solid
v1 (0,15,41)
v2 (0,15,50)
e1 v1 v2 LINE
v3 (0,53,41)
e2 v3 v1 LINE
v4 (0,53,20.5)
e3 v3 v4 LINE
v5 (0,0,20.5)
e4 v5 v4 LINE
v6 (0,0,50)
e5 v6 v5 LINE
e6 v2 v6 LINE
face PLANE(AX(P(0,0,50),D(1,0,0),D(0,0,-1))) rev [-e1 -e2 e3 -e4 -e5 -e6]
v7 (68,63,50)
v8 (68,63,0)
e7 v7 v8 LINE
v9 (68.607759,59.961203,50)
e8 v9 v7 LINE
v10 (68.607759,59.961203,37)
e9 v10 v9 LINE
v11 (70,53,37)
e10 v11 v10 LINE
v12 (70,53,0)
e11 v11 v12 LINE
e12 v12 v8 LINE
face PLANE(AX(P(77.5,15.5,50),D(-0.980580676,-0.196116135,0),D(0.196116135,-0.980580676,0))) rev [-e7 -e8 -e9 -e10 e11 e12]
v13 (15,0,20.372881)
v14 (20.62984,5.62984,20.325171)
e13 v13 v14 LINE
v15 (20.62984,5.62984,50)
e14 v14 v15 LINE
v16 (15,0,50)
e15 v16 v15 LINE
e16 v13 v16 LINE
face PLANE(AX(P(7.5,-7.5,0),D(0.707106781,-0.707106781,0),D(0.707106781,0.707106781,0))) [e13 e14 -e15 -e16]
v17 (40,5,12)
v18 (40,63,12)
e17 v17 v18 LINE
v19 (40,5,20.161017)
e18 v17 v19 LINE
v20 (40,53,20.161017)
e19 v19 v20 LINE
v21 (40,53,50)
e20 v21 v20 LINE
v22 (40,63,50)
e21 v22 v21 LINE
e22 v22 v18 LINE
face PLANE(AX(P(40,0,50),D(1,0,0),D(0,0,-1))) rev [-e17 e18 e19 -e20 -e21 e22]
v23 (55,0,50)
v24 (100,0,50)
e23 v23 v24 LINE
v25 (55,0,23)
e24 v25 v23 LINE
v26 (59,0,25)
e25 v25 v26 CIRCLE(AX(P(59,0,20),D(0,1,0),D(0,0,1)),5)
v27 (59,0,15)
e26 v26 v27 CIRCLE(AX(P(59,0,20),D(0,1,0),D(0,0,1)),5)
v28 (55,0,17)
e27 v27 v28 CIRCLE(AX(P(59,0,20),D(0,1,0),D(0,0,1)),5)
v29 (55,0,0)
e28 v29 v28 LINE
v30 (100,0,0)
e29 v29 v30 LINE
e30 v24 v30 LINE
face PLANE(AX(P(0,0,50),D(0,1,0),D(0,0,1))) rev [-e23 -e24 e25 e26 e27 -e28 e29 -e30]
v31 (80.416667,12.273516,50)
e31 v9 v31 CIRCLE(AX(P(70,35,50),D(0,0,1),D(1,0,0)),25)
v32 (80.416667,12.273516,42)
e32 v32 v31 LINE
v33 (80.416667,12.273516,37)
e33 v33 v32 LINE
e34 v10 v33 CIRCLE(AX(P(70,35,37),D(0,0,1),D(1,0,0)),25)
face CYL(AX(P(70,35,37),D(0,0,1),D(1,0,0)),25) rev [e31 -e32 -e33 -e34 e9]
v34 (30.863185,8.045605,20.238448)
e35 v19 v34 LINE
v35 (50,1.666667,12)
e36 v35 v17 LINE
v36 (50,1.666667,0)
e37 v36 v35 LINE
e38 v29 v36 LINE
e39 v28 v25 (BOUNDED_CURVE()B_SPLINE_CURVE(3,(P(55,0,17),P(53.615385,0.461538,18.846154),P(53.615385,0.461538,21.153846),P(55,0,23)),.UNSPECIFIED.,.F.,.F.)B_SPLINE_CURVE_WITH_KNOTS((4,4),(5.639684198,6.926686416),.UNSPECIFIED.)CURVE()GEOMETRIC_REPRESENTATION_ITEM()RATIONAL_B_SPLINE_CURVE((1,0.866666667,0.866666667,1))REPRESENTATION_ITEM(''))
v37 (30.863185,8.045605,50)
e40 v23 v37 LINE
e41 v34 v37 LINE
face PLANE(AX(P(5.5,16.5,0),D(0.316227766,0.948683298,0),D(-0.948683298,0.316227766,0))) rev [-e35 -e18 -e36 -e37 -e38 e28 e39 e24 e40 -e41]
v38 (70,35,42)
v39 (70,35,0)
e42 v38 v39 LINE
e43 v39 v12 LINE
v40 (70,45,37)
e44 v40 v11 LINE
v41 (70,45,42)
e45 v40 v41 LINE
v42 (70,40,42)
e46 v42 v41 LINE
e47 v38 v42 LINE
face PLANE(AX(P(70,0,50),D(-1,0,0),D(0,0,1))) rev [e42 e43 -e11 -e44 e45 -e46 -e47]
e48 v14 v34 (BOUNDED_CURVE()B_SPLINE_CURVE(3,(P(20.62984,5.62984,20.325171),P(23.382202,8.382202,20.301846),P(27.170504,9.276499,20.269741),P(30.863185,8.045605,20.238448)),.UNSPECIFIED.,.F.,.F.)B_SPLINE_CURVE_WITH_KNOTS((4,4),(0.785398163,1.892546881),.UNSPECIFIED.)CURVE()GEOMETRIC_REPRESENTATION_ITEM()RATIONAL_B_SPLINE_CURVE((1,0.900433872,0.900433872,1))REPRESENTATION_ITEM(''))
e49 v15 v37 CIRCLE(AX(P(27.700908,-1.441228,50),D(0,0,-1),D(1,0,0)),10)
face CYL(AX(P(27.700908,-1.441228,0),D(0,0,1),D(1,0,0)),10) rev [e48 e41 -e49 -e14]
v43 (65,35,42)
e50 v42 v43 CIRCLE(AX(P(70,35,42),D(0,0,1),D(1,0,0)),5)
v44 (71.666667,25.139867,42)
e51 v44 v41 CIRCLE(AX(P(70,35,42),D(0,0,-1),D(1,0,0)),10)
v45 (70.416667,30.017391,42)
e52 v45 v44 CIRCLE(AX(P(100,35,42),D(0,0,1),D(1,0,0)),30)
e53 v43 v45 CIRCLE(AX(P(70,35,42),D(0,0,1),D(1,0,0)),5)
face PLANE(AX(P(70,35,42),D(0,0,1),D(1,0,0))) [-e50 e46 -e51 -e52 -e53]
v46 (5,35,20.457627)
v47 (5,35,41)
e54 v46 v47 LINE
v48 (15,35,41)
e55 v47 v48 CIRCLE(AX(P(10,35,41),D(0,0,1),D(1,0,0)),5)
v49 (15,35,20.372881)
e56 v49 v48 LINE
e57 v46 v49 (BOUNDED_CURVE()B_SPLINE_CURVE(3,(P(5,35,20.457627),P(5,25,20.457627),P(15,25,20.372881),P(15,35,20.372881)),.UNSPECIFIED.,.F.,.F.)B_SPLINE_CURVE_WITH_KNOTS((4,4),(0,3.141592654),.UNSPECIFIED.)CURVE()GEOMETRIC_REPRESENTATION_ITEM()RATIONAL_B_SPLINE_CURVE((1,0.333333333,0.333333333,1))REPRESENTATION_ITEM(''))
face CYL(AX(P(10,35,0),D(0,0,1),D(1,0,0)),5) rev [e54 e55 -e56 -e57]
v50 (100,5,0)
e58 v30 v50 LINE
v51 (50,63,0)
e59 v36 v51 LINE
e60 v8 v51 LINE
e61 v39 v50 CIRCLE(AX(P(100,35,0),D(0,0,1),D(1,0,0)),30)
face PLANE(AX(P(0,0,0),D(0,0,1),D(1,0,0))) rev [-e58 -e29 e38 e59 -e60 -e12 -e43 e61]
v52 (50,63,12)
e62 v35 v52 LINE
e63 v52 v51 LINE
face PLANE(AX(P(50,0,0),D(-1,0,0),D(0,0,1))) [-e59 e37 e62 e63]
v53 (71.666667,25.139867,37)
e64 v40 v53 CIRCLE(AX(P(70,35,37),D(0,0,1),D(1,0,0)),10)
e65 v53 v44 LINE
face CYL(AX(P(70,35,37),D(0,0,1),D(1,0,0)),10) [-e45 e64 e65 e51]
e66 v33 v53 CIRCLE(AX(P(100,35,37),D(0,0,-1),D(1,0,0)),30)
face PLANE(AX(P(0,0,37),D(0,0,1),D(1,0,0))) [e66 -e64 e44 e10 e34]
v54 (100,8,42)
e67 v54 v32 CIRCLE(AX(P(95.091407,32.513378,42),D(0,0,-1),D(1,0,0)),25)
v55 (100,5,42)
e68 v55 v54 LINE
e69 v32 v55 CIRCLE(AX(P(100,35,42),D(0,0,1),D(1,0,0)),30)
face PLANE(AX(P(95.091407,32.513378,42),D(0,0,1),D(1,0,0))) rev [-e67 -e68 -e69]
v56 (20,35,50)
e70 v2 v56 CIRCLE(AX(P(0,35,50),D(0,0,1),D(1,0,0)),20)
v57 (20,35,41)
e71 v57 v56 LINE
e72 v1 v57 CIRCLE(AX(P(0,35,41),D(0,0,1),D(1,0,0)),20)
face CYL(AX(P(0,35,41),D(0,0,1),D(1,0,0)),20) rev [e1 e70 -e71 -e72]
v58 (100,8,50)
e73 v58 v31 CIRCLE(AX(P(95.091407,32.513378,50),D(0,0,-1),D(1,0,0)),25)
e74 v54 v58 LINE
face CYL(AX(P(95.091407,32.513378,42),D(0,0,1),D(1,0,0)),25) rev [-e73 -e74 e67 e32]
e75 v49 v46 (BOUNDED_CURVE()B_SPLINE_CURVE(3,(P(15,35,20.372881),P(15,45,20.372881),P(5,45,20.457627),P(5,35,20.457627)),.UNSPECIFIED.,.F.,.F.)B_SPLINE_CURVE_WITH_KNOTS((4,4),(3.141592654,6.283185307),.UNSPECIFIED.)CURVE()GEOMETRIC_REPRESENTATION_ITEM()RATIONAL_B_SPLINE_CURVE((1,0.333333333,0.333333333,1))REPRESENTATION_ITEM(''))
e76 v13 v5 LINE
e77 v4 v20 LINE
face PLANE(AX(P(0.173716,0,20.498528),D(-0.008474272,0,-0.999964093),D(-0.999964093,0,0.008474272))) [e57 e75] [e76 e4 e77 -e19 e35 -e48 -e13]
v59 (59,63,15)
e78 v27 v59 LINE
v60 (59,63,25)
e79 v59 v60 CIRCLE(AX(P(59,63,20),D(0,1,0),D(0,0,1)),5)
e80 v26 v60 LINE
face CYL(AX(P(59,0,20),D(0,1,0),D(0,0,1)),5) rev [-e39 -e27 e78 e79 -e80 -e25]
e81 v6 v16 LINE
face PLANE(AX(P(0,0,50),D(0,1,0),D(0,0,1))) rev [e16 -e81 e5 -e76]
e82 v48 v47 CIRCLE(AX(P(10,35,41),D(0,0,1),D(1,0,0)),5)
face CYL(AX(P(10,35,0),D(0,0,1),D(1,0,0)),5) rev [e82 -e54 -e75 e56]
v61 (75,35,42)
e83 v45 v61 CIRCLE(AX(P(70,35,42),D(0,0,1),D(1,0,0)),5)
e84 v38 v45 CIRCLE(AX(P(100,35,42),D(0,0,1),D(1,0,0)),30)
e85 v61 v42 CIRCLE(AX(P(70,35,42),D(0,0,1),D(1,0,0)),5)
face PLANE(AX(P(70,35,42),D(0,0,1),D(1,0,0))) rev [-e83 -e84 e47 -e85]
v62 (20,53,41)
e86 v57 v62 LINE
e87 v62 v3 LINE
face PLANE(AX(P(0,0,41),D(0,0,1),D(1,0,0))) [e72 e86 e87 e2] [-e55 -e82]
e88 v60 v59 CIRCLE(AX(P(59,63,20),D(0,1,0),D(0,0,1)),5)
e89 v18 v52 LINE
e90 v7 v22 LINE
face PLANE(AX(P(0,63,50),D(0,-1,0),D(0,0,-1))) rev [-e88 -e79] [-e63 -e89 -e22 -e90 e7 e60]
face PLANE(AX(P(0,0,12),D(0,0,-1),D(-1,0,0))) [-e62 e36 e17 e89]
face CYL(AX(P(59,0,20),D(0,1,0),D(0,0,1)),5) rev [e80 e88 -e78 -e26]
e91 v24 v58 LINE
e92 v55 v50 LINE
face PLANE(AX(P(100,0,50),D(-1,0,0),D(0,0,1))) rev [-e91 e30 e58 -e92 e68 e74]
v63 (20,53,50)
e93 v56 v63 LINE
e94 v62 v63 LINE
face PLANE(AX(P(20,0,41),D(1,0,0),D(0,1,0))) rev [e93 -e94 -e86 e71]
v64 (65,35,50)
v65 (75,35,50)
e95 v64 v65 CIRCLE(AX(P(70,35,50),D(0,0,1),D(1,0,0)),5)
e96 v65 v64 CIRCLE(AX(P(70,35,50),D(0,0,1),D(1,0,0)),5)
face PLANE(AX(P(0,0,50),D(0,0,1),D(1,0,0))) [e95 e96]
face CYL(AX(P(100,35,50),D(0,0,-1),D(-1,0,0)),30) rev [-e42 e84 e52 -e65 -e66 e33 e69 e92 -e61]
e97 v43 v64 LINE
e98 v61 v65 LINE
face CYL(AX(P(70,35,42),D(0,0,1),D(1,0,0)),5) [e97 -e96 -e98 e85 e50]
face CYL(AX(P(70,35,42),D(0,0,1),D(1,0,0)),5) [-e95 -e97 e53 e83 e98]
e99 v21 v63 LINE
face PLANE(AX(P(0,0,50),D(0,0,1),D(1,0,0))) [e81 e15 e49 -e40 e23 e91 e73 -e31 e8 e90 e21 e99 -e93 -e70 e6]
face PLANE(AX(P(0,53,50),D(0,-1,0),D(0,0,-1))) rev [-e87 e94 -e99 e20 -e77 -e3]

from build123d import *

# Parameters (mm, degrees)
BLOCK_BODY_DEPTH          = 50
BEARING_START             = -13
BEARING_ARC_RECESS_DEPTH  = 13
ARC_POCKET_SKETCH_R       = 10.03476875
ARC_POCKET_SKETCH_R_2     = 5
ARC_POCKET_DEPTH          = 8
PIN_10_SKETCH_R           = 5
PIN_10_DEPTH              = 8
SIDE_BOSS_DEPTH           = 8
PROFILE_RELIEF_CUT_DEPTH  = 129.33160172
STEP_CUT_DEPTH            = 9
STEP_NOTCH_DEPTH          = 126.099960032
SLOT_CUT_SKETCH_R         = 5
SLOT_CUT_DEPTH            = 129.33160172
TOP_RELIEF_CUT_DEPTH      = 129.33160172
TOP_RELIEF_CUT_DEPTH_BACK = 129.33160172
TOP_RELIEF_SKETCH_W       = 10
TOP_RELIEF_SKETCH_H       = 12


with BuildPart() as part:
    # Block Profile Sketch → Block Body (new body)
    with BuildSketch(Plane.XY):
        with BuildLine():
            ThreePointArc((70, 35), (78.786796564, 13.786796564), (100, 5))
            Line((100, 5), (100, 0))
            Line((100, 0), (0, 0))
            Line((0, 0), (0, 53))
            Line((0, 53), (40, 53))
            Line((40, 53), (40, 63))
            Line((40, 63), (50, 63))
            Line((50, 63), (68, 63))
            Line((68, 63), (70, 53))
            Line((70, 53), (70, 35))
        make_face()
    extrude(amount=BLOCK_BODY_DEPTH)

    # Bearing Arc Recess Sketch → Bearing Arc Recess (cut)
    with BuildSketch(Plane.XY.offset(50).offset(BEARING_START)):
        with BuildLine():
            ThreePointArc((80.416666667, 12.273516428), (91.040635288, 21.498456878), (95, 35))
            ThreePointArc((95, 35), (87.17838735, 53.163232313), (68.607759357, 59.961203216))
            Line((68.607759357, 59.961203216), (70, 53))
            Line((70, 53), (70, 45))
            ThreePointArc((70, 45), (77.071067812, 42.071067812), (80, 35))
            ThreePointArc((80, 35), (77.637626158, 28.545027756), (71.666666667, 25.139867028))
            ThreePointArc((71.666666667, 25.139867028), (75.192995333, 18.129537071), (80.416666667, 12.273516428))
        make_face()
        with BuildLine():
            Line((70, 53), (68.607759357, 59.961203216))
            ThreePointArc((68.607759357, 59.961203216), (45.732966105, 28.990751633), (80.416666667, 12.273516428))
            ThreePointArc((80.416666667, 12.273516428), (75.192995333, 18.129537071), (71.666666667, 25.139867028))
            ThreePointArc((71.666666667, 25.139867028), (60.035028105, 34.163737397), (70, 45))
            Line((70, 45), (70, 53))
        make_face()
    extrude(amount=BEARING_ARC_RECESS_DEPTH, mode=Mode.SUBTRACT)

    # Arc Pocket Sketch → Arc Pocket (cut)
    with BuildSketch(Plane.XY.offset(50)):
        with Locations((70, 35)):
            Circle(ARC_POCKET_SKETCH_R)
        with Locations((70, 35)):
            Circle(ARC_POCKET_SKETCH_R_2, mode=Mode.SUBTRACT)
    extrude(amount=-ARC_POCKET_DEPTH, mode=Mode.SUBTRACT)

    # Pin Ø10 Sketch → Pin Ø10 (add)
    with BuildSketch(Plane.XY.offset(50)):
        with Locations((70, 35)):
            Circle(PIN_10_SKETCH_R)
    extrude(amount=-PIN_10_DEPTH)

    # Side Boss Sketch → Side Boss (add)
    with BuildSketch(Plane.XY.offset(50)):
        with BuildLine():
            Line((80.416666667, 12.273516428), (80.416666667, 0))
            Line((80.416666667, 0), (100, 0))
            Line((100, 0), (100, 8))
            ThreePointArc((100, 8), (89.761290268, 8.088189193), (80.416666667, 12.273516428))
        make_face()
    extrude(amount=-SIDE_BOSS_DEPTH)

    # Profile Relief Sketch → Profile Relief Cut (cut, through all)
    with BuildSketch(Plane.XY.offset(50)):
        with BuildLine():
            Line((20.629839756, 5.629839756), (15, 0))
            Line((15, 0), (25, 0))
            Line((25, 0), (55, 0))
            Line((55, 0), (30.863185228, 8.045604924))
            ThreePointArc((30.863185228, 8.045604924), (25.403378362, 8.291261838), (20.629839756, 5.629839756))
        make_face()
    extrude(amount=-PROFILE_RELIEF_CUT_DEPTH, mode=Mode.SUBTRACT)

    # Step Cut Sketch → Step Cut (cut)
    with BuildSketch(Plane.XY.offset(50)):
        with BuildLine():
            Line((0, 35), (20, 35))
            ThreePointArc((20, 35), (16.946326412, 45.621771092), (8.717797887, 53))
            Line((8.717797887, 53), (0, 53))
            Line((0, 53), (0, 35))
        make_face()
        with BuildLine():
            ThreePointArc((8.717797887, 53), (16.946326412, 45.621771092), (20, 35))
            Line((20, 35), (20, 53))
            Line((20, 53), (8.717797887, 53))
        make_face()
        with BuildLine():
            ThreePointArc((0, 15), (14.142135624, 20.857864376), (20, 35))
            Line((20, 35), (0, 35))
            Line((0, 35), (0, 15))
        make_face()
    extrude(amount=-STEP_CUT_DEPTH, mode=Mode.SUBTRACT)

    # Step Notch Sketch → Step Notch (cut, through all)
    with BuildSketch(Plane.XY.offset(41)):
        with BuildLine():
            ThreePointArc((10, 40), (6.464466094, 31.464466094), (15, 35))
            Line((15, 35), (10, 35))
            Line((10, 35), (10, 40))
        make_face()
        with BuildLine():
            Line((10, 35), (15, 35))
            ThreePointArc((15, 35), (13.535533906, 38.535533906), (10, 40))
            Line((10, 40), (10, 35))
        make_face()
    extrude(amount=-STEP_NOTCH_DEPTH, mode=Mode.SUBTRACT)

    # Slot Cut Sketch → Slot Cut (cut, through all)
    with BuildSketch(Plane(origin=(0, 63, 0), x_dir=(1, 0, 0), z_dir=(0, 1, 0))):
        with Locations(Location((59, -20, 0), (0, 0, 270))):
            Circle(SLOT_CUT_SKETCH_R)
    extrude(amount=-SLOT_CUT_DEPTH, mode=Mode.SUBTRACT)

    # Top Relief Sketch → Top Relief Cut (cut, two sides: drawn at the far end of the back side and taken through both)
    with BuildSketch(Plane(origin=(0, 63, 0), x_dir=(1, 0, 0), z_dir=(0, 1, 0)).offset(-TOP_RELIEF_CUT_DEPTH_BACK)):
        with Locations((45, -6)):
            Rectangle(TOP_RELIEF_SKETCH_W, TOP_RELIEF_SKETCH_H)
        Polygon((40, -12), (40, 0), (0, 0), (0, -20.5), (40, -20.161016949), align=None)
    extrude(amount=TOP_RELIEF_CUT_DEPTH + TOP_RELIEF_CUT_DEPTH_BACK, mode=Mode.SUBTRACT)


solid = part.part
